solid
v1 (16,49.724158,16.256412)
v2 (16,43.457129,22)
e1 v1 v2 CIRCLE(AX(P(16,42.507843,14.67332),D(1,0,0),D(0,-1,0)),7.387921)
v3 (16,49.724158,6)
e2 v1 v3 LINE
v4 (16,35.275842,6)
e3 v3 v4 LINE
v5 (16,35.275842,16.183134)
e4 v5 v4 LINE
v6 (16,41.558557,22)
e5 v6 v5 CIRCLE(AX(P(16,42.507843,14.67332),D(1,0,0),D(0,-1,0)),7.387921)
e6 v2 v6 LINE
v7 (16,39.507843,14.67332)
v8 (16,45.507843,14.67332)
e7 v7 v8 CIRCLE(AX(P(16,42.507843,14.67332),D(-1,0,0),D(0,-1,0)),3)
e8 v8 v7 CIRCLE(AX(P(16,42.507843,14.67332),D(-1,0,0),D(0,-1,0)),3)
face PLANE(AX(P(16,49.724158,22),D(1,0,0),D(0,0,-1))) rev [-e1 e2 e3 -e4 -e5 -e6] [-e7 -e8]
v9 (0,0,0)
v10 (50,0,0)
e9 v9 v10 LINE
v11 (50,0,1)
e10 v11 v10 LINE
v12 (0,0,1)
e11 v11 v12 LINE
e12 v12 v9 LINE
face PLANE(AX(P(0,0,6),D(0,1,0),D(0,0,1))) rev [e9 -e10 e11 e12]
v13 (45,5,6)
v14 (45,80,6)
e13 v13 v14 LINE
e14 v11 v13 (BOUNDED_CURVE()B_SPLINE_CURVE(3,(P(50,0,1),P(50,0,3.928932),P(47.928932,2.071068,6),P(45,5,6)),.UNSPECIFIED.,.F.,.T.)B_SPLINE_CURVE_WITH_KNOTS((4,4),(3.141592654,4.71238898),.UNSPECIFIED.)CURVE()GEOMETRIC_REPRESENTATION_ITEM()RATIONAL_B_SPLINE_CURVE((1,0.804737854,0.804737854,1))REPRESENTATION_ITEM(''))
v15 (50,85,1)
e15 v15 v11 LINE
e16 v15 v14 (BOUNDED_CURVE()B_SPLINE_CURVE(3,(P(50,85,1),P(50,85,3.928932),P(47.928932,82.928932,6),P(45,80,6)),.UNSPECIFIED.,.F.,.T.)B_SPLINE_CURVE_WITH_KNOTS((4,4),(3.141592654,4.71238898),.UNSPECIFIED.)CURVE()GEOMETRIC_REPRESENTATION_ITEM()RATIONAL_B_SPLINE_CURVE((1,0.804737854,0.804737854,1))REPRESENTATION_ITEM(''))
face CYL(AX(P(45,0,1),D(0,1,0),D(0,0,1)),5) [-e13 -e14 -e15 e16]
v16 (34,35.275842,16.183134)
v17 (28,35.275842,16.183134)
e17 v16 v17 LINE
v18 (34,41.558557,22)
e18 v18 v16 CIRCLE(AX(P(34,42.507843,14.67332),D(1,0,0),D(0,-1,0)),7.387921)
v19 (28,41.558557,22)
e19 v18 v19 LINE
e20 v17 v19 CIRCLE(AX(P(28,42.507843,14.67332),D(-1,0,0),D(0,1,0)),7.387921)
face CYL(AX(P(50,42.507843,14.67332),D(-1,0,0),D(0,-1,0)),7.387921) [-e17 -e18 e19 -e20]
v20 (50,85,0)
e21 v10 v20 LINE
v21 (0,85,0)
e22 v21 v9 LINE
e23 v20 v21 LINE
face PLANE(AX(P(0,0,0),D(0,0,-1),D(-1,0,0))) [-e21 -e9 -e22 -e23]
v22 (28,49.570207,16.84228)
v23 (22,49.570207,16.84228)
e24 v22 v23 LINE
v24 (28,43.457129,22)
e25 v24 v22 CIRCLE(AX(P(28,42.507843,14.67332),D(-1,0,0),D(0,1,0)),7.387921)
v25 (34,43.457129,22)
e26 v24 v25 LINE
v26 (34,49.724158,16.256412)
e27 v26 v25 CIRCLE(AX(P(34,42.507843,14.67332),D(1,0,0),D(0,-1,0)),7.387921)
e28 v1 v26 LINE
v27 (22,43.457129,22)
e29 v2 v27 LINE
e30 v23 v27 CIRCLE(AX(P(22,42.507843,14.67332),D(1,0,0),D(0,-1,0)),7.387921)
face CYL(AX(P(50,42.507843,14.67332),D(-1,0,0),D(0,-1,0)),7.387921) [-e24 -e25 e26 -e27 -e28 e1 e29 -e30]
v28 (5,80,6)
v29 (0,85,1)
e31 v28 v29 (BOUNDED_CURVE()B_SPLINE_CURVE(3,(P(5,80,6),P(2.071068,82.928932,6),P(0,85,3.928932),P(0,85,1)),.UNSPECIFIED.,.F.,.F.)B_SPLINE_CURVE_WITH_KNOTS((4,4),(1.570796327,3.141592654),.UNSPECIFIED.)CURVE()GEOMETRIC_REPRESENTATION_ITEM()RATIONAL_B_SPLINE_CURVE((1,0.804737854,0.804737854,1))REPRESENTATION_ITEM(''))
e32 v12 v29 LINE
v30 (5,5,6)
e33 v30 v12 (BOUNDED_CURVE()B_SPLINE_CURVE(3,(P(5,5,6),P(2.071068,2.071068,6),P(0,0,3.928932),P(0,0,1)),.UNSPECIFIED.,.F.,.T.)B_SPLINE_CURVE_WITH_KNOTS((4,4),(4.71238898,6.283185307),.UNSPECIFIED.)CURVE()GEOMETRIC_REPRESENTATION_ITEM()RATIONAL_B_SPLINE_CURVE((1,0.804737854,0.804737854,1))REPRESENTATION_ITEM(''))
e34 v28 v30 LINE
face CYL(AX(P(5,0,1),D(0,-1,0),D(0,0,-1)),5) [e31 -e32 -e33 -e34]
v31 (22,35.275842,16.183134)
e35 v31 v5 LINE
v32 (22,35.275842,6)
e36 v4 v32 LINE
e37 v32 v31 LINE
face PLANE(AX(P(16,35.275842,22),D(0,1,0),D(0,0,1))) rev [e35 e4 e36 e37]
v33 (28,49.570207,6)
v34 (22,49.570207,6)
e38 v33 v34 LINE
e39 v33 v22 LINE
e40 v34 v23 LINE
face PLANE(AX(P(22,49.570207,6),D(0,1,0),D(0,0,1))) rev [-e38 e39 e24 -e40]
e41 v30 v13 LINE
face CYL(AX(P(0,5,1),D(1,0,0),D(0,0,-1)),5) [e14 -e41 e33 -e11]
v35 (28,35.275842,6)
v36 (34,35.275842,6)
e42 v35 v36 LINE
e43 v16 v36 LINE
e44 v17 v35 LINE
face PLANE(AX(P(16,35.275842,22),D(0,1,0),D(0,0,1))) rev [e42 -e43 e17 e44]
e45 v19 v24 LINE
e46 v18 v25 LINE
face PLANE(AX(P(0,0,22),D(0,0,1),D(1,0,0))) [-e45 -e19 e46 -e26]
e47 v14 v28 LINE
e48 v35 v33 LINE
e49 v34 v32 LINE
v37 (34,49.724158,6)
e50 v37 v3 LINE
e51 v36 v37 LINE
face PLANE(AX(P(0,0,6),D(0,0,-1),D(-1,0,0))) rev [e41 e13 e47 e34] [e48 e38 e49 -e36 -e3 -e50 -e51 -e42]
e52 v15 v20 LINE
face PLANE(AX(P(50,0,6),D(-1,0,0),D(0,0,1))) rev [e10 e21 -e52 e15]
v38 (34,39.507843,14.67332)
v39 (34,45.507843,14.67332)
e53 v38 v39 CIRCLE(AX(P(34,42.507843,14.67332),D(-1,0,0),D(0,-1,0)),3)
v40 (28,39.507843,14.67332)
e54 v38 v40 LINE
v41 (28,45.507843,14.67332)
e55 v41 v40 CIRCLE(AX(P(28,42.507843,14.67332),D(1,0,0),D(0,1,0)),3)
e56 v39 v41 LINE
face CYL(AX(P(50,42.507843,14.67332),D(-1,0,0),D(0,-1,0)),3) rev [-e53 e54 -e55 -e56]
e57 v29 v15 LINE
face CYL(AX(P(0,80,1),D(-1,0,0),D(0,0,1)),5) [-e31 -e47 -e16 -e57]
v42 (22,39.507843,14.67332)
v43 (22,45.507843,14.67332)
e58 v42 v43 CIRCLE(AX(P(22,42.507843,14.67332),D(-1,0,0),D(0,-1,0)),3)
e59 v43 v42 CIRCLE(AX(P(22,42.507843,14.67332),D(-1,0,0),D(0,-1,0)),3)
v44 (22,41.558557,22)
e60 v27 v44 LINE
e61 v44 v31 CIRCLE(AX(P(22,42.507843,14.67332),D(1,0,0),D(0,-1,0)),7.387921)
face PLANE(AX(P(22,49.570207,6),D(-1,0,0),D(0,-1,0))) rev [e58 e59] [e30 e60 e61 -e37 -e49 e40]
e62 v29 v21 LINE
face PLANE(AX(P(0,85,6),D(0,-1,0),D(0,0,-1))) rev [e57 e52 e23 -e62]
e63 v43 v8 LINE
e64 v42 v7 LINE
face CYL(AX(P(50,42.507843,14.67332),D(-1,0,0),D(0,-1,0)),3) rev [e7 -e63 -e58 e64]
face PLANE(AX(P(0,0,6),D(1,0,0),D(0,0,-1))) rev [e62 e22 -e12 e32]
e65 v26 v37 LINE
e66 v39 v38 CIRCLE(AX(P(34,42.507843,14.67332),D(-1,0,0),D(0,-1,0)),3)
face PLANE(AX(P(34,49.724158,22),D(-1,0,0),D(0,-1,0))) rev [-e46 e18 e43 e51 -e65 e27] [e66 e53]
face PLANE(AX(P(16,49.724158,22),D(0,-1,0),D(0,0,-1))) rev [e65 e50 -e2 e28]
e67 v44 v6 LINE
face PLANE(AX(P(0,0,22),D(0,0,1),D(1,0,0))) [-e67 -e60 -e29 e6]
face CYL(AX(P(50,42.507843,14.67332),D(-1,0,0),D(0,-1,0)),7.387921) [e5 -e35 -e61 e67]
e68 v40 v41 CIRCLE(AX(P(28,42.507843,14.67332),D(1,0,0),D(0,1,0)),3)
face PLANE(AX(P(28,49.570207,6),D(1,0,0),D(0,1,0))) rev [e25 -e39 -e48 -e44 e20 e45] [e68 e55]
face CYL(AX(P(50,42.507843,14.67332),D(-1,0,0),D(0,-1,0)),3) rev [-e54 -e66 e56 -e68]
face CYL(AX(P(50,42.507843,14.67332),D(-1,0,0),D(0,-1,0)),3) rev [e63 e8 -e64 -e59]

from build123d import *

# Parameters (mm, degrees)
SKETCH1_W           = 50
SKETCH1_H           = 85
BOSS_EXTRUDE1_DEPTH = 6
SKETCH2_W           = 18
SKETCH2_H           = 14.448315912
BOSS_EXTRUDE2_DEPTH = 16
FILLET1_R           = 5
SKETCH3_W           = 6
SKETCH3_H           = 29.716496746
CUT_EXTRUDE1_DEPTH  = 16
SKETCH4_R           = 3
CUT_EXTRUDE2_DEPTH  = 95.154128959


with BuildPart() as part:
    # Sketch1 → Boss-Extrude1 (new body)
    with BuildSketch(Plane.XY):
        with Locations((25, 42.5)):
            Rectangle(SKETCH1_W, SKETCH1_H)
    extrude(amount=BOSS_EXTRUDE1_DEPTH)

    # Sketch2 → Boss-Extrude2 (add)
    with BuildSketch(Plane.XY.offset(6)):
        with Locations((25, 42.5)):
            Rectangle(SKETCH2_W, SKETCH2_H)
    extrude(amount=BOSS_EXTRUDE2_DEPTH)

    # Fillet1
    fillet1_edges = [part.edges().sort_by_distance(p)[0] for p in [
        (50, 42.5, 6),
        (25, 85, 6),
        (0, 42.5, 6),
        (25, 0, 6),
    ]]
    fillet(fillet1_edges, radius=FILLET1_R)

    # Sketch3 → Cut-Extrude1 (cut)
    with BuildSketch(Plane.XY.offset(22)):
        with Locations((25, 34.711959109)):
            Rectangle(SKETCH3_W, SKETCH3_H)
    extrude(amount=-CUT_EXTRUDE1_DEPTH, mode=Mode.SUBTRACT)

    # Sketch4 → Cut-Extrude2 (cut, through all)
    with BuildSketch(Plane.ZY.offset(-16)):
        with Locations(Location((14.673320443, 42.507843144, 0), (0, 0, 270))):
            Circle(SKETCH4_R)
        with BuildLine():
            Line((14.673320443, 49.895764166), (20.802104858, 55.115800091))
            Line((20.802104858, 55.115800091), (35.798114719, 48.402784846))
            Line((35.798114719, 48.402784846), (20.212830652, 12.710723094))
            Line((20.212830652, 12.710723094), (14.673320443, 35.119922122))
            ThreePointArc((14.673320443, 35.119922122), (22.061241465, 42.507843144), (14.673320443, 49.895764166))
        make_face()
    extrude(amount=-CUT_EXTRUDE2_DEPTH, mode=Mode.SUBTRACT)


solid = part.part
